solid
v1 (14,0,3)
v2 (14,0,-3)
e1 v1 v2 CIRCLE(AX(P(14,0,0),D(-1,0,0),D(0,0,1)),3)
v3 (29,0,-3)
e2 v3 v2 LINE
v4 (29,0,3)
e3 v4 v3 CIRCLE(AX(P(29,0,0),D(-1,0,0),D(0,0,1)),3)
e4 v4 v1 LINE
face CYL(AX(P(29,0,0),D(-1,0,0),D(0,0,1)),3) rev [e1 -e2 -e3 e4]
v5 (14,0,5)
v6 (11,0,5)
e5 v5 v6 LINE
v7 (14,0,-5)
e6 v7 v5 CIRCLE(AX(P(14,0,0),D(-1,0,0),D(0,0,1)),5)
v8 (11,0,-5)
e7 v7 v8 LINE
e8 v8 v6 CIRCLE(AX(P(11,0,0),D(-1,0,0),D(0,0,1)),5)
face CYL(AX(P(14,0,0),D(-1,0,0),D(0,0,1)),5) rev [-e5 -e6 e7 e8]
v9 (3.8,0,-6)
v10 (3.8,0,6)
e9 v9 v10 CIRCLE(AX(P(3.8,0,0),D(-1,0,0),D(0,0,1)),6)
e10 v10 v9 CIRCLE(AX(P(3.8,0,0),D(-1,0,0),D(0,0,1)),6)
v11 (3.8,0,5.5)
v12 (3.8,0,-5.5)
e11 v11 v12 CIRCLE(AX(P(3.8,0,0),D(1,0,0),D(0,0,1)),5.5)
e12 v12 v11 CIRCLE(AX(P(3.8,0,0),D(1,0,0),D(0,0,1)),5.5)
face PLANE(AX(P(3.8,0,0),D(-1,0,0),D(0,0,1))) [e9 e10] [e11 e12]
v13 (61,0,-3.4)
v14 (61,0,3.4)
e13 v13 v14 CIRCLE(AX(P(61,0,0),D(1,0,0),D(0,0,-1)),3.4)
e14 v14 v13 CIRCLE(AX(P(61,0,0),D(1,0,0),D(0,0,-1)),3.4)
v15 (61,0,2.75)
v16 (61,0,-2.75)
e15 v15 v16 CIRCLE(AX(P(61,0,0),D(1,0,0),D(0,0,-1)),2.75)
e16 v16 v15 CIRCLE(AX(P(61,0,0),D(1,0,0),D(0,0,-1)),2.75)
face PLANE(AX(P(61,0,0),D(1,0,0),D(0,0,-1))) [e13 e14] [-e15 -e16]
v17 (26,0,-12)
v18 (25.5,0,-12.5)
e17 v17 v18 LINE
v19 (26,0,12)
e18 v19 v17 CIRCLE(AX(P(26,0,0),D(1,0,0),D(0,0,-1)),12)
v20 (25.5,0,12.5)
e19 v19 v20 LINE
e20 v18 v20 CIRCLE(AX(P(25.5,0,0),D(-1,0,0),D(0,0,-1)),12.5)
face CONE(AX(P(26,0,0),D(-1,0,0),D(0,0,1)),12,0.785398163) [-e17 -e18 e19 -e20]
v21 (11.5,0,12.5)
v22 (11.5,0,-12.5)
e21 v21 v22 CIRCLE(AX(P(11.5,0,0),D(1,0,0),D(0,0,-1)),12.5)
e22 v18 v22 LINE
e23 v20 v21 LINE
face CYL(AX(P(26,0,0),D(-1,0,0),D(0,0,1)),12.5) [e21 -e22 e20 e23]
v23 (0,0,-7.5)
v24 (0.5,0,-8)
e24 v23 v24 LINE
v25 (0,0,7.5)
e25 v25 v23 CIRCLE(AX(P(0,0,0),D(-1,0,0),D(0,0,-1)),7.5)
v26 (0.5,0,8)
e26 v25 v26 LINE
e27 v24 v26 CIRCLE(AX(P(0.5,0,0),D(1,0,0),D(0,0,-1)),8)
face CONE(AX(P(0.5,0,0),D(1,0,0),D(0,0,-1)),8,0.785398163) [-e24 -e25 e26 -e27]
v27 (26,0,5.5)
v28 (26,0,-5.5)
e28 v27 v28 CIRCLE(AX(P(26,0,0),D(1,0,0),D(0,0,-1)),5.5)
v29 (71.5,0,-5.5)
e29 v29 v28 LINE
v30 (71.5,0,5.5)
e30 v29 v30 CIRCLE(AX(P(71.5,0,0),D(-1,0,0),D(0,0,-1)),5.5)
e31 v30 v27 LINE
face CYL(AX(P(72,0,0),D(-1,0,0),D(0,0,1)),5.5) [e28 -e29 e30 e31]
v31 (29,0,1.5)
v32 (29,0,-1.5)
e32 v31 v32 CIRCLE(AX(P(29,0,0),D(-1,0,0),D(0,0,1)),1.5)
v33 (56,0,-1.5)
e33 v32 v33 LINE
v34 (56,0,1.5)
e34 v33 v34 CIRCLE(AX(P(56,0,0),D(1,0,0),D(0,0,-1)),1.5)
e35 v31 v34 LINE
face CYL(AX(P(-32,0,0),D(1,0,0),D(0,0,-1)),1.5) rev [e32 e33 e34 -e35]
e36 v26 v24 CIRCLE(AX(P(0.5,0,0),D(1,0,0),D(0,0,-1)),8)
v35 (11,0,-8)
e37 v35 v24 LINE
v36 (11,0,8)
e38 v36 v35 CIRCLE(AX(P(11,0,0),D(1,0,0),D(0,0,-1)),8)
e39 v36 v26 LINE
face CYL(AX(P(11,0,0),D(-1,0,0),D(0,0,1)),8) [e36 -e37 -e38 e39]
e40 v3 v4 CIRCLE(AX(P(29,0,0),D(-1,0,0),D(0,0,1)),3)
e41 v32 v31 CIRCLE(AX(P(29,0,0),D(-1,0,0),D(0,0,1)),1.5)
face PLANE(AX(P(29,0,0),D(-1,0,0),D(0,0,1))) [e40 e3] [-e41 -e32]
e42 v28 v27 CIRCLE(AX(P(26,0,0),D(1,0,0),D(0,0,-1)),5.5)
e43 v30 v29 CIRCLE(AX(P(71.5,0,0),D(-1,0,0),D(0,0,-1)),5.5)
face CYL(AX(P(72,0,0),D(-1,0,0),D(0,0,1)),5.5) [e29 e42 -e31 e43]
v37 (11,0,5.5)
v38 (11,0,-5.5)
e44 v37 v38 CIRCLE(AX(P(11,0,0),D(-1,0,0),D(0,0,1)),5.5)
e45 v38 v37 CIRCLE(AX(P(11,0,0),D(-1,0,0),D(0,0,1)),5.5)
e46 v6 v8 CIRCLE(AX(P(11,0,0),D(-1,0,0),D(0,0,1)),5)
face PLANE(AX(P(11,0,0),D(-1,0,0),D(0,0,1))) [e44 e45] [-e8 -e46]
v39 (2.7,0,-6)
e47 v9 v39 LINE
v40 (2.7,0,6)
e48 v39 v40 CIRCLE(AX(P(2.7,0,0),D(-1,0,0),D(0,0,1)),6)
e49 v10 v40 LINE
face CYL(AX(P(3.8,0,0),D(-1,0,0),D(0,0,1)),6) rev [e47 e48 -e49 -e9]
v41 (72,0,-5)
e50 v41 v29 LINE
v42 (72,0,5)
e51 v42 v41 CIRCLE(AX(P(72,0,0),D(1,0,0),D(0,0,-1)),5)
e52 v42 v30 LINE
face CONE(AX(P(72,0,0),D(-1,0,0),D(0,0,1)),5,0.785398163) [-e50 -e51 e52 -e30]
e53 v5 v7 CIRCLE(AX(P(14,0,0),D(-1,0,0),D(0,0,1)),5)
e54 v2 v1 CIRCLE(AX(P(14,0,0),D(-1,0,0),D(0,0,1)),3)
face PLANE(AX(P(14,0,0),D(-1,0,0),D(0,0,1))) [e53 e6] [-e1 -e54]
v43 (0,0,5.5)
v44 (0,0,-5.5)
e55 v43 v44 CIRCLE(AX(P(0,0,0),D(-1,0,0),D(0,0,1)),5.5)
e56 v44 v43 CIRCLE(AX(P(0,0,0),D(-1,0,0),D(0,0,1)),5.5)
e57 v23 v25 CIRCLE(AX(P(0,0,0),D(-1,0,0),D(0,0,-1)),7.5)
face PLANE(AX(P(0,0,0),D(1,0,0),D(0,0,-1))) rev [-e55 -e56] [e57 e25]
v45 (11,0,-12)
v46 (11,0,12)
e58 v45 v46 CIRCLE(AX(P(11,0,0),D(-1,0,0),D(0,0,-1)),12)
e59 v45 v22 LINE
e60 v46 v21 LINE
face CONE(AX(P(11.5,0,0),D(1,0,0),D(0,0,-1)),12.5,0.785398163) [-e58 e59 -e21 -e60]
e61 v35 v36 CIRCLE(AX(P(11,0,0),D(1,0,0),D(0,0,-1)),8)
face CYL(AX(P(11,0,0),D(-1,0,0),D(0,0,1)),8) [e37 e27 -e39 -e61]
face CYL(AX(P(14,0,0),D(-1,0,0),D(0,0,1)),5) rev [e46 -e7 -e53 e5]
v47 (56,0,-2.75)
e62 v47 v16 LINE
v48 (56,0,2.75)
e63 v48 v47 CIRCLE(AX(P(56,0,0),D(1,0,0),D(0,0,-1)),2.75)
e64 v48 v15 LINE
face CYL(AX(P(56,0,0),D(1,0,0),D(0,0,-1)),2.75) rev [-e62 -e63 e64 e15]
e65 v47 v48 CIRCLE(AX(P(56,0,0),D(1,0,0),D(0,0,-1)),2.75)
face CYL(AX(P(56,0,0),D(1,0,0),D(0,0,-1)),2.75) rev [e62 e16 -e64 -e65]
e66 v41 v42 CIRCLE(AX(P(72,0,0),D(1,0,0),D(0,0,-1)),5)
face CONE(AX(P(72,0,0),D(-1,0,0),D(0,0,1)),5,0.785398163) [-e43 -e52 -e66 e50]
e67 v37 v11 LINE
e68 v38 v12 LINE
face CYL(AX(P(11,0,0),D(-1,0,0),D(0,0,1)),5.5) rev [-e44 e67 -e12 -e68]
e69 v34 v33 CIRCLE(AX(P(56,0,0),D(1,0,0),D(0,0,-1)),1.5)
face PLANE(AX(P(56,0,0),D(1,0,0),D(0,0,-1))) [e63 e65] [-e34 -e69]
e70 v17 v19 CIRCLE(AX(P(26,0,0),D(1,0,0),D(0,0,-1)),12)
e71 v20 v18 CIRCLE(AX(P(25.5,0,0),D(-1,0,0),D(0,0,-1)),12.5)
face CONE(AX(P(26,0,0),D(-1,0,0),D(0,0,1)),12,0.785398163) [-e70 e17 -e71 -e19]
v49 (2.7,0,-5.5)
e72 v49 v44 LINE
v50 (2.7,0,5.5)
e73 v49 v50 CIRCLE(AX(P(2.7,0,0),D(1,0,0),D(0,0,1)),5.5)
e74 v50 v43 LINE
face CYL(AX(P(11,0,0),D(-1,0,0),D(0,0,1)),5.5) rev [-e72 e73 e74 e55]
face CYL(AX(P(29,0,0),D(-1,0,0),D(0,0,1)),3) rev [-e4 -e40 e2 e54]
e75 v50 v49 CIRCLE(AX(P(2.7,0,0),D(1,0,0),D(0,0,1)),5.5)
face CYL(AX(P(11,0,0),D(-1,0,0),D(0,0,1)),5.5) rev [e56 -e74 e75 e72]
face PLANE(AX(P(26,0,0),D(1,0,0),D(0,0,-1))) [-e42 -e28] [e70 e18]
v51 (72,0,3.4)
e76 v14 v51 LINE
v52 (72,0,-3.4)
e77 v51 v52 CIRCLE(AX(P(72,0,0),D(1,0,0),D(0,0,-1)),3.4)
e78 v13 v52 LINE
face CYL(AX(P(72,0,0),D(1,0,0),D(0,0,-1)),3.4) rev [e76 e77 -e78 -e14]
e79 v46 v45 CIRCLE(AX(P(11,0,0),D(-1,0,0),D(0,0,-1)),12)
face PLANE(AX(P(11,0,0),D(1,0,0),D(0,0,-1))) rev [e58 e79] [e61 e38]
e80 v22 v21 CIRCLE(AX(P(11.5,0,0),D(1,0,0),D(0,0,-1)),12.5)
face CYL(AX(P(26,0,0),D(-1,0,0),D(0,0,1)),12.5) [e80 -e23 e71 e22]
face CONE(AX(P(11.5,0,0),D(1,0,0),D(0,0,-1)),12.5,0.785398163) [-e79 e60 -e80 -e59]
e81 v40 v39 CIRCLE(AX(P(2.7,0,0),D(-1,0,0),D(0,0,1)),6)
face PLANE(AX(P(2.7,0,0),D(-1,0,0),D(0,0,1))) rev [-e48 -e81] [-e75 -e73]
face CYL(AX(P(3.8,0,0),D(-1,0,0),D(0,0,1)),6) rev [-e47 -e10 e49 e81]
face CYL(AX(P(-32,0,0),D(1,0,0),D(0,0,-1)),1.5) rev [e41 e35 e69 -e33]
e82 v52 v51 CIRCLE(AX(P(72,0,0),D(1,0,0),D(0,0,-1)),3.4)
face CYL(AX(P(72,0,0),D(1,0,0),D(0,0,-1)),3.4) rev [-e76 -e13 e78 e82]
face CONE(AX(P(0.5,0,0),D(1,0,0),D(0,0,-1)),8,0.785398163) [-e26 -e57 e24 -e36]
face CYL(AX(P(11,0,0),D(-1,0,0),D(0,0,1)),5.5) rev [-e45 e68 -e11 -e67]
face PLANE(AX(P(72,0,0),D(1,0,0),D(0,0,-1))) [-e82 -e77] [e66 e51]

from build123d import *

# Parameters (mm, degrees)
SKETCH1_R             = 8
BOSS_EXTRUDE1_DEPTH   = 11
SKETCH2_R             = 12.5
BOSS_EXTRUDE2_DEPTH   = 15
SKETCH3_R             = 5.5
BOSS_EXTRUDE3_DEPTH   = 46
SKETCH5_R             = 5.5
CUT_EXTRUDE1_DEPTH    = 11
CUT_EXTRUDE2_START    = -2.7
SKETCH6_R             = 6
CUT_EXTRUDE2_DEPTH    = 1.1
SKETCH7_R             = 5
CUT_EXTRUDE3_DEPTH    = 10.2
SKETCH8_R             = 3
CUT_EXTRUDE4_DEPTH    = 15
M8_TAPPED_HOLE1_D     = 6.8
M8_TAPPED_HOLE1_DEPTH = 11
M8_TAPPED_HOLE1_TIP   = 2.042926105
BOSS_EXTRUDE4_START   = -16
SKETCH11_R            = 5.5
BOSS_EXTRUDE4_DEPTH   = 5
SKETCH12_R            = 2.75
CUT_EXTRUDE5_DEPTH    = 5
SKETCH13_R            = 1.5
CUT_EXTRUDE6_DEPTH    = 88
CHAMFER1_SIZE         = 0.5


with BuildPart() as part:
    # Sketch1 → Boss-Extrude1 (new body)
    with BuildSketch(Plane(origin=(0, 0, 0), x_dir=(0, 0, -1), z_dir=(1, 0, 0))):
        Circle(SKETCH1_R)
    extrude(amount=BOSS_EXTRUDE1_DEPTH)

    # Sketch2 → Boss-Extrude2 (add)
    with BuildSketch(Plane(origin=(11, 0, 0), x_dir=(0, 0, -1), z_dir=(1, 0, 0))):
        Circle(SKETCH2_R)
    extrude(amount=BOSS_EXTRUDE2_DEPTH)

    # Sketch3 → Boss-Extrude3 (add)
    with BuildSketch(Plane(origin=(26, 0, 0), x_dir=(0, 0, -1), z_dir=(1, 0, 0))):
        Circle(SKETCH3_R)
    extrude(amount=BOSS_EXTRUDE3_DEPTH)

    # Sketch5 → Cut-Extrude1 (cut)
    with BuildSketch(Plane.ZY):
        with Locations(Location((0, 0, 0), (0, 0, 180))):
            Circle(SKETCH5_R)
    extrude(amount=-CUT_EXTRUDE1_DEPTH, mode=Mode.SUBTRACT)

    # Sketch6 → Cut-Extrude2 (cut)
    with BuildSketch(Plane.ZY.offset(CUT_EXTRUDE2_START)):
        Circle(SKETCH6_R)
    extrude(amount=-CUT_EXTRUDE2_DEPTH, mode=Mode.SUBTRACT)

    # Sketch7 → Cut-Extrude3 (cut)
    with BuildSketch(Plane.ZY.offset(-3.8)):
        Circle(SKETCH7_R)
    extrude(amount=-CUT_EXTRUDE3_DEPTH, mode=Mode.SUBTRACT)

    # Sketch8 → Cut-Extrude4 (cut)
    with BuildSketch(Plane.ZY.offset(-14)):
        Circle(SKETCH8_R)
    extrude(amount=-CUT_EXTRUDE4_DEPTH, mode=Mode.SUBTRACT)

    # M8 Tapped Hole1
    with Locations(Plane(origin=(72, 0, 0), x_dir=(0, 0, -1), z_dir=(1, 0, 0))):
        with Locations((0, 0)):
            Hole(M8_TAPPED_HOLE1_D / 2, depth=M8_TAPPED_HOLE1_DEPTH)
            with Locations((0, 0, -(M8_TAPPED_HOLE1_DEPTH + M8_TAPPED_HOLE1_TIP / 2))):  # 118° drill point
                Cone(0, M8_TAPPED_HOLE1_D / 2, M8_TAPPED_HOLE1_TIP, mode=Mode.SUBTRACT)

    # Sketch11 → Boss-Extrude4 (add)
    with BuildSketch(Plane(origin=(72, 0, 0), x_dir=(0, 0, -1), z_dir=(1, 0, 0)).offset(BOSS_EXTRUDE4_START)):
        Circle(SKETCH11_R)
    extrude(amount=BOSS_EXTRUDE4_DEPTH)

    # Sketch12 → Cut-Extrude5 (cut)
    with BuildSketch(Plane(origin=(61, 0, 0), x_dir=(0, 0, -1), z_dir=(1, 0, 0))):
        Circle(SKETCH12_R)
    extrude(amount=-CUT_EXTRUDE5_DEPTH, mode=Mode.SUBTRACT)

    # Sketch13 → Cut-Extrude6 (cut)
    with BuildSketch(Plane(origin=(56, 0, 0), x_dir=(0, 0, -1), z_dir=(1, 0, 0))):
        Circle(SKETCH13_R)
    extrude(amount=-CUT_EXTRUDE6_DEPTH, mode=Mode.SUBTRACT)

    # Chamfer1
    chamfer1_edges = [part.edges().sort_by_distance(p)[0] for p in [
        (72, 0, 5.5),
        (0, 0, 8),
        (11, 0, 12.5),
        (26, 0, 12.5),
    ]]
    chamfer(chamfer1_edges, length=CHAMFER1_SIZE)


solid = part.part
